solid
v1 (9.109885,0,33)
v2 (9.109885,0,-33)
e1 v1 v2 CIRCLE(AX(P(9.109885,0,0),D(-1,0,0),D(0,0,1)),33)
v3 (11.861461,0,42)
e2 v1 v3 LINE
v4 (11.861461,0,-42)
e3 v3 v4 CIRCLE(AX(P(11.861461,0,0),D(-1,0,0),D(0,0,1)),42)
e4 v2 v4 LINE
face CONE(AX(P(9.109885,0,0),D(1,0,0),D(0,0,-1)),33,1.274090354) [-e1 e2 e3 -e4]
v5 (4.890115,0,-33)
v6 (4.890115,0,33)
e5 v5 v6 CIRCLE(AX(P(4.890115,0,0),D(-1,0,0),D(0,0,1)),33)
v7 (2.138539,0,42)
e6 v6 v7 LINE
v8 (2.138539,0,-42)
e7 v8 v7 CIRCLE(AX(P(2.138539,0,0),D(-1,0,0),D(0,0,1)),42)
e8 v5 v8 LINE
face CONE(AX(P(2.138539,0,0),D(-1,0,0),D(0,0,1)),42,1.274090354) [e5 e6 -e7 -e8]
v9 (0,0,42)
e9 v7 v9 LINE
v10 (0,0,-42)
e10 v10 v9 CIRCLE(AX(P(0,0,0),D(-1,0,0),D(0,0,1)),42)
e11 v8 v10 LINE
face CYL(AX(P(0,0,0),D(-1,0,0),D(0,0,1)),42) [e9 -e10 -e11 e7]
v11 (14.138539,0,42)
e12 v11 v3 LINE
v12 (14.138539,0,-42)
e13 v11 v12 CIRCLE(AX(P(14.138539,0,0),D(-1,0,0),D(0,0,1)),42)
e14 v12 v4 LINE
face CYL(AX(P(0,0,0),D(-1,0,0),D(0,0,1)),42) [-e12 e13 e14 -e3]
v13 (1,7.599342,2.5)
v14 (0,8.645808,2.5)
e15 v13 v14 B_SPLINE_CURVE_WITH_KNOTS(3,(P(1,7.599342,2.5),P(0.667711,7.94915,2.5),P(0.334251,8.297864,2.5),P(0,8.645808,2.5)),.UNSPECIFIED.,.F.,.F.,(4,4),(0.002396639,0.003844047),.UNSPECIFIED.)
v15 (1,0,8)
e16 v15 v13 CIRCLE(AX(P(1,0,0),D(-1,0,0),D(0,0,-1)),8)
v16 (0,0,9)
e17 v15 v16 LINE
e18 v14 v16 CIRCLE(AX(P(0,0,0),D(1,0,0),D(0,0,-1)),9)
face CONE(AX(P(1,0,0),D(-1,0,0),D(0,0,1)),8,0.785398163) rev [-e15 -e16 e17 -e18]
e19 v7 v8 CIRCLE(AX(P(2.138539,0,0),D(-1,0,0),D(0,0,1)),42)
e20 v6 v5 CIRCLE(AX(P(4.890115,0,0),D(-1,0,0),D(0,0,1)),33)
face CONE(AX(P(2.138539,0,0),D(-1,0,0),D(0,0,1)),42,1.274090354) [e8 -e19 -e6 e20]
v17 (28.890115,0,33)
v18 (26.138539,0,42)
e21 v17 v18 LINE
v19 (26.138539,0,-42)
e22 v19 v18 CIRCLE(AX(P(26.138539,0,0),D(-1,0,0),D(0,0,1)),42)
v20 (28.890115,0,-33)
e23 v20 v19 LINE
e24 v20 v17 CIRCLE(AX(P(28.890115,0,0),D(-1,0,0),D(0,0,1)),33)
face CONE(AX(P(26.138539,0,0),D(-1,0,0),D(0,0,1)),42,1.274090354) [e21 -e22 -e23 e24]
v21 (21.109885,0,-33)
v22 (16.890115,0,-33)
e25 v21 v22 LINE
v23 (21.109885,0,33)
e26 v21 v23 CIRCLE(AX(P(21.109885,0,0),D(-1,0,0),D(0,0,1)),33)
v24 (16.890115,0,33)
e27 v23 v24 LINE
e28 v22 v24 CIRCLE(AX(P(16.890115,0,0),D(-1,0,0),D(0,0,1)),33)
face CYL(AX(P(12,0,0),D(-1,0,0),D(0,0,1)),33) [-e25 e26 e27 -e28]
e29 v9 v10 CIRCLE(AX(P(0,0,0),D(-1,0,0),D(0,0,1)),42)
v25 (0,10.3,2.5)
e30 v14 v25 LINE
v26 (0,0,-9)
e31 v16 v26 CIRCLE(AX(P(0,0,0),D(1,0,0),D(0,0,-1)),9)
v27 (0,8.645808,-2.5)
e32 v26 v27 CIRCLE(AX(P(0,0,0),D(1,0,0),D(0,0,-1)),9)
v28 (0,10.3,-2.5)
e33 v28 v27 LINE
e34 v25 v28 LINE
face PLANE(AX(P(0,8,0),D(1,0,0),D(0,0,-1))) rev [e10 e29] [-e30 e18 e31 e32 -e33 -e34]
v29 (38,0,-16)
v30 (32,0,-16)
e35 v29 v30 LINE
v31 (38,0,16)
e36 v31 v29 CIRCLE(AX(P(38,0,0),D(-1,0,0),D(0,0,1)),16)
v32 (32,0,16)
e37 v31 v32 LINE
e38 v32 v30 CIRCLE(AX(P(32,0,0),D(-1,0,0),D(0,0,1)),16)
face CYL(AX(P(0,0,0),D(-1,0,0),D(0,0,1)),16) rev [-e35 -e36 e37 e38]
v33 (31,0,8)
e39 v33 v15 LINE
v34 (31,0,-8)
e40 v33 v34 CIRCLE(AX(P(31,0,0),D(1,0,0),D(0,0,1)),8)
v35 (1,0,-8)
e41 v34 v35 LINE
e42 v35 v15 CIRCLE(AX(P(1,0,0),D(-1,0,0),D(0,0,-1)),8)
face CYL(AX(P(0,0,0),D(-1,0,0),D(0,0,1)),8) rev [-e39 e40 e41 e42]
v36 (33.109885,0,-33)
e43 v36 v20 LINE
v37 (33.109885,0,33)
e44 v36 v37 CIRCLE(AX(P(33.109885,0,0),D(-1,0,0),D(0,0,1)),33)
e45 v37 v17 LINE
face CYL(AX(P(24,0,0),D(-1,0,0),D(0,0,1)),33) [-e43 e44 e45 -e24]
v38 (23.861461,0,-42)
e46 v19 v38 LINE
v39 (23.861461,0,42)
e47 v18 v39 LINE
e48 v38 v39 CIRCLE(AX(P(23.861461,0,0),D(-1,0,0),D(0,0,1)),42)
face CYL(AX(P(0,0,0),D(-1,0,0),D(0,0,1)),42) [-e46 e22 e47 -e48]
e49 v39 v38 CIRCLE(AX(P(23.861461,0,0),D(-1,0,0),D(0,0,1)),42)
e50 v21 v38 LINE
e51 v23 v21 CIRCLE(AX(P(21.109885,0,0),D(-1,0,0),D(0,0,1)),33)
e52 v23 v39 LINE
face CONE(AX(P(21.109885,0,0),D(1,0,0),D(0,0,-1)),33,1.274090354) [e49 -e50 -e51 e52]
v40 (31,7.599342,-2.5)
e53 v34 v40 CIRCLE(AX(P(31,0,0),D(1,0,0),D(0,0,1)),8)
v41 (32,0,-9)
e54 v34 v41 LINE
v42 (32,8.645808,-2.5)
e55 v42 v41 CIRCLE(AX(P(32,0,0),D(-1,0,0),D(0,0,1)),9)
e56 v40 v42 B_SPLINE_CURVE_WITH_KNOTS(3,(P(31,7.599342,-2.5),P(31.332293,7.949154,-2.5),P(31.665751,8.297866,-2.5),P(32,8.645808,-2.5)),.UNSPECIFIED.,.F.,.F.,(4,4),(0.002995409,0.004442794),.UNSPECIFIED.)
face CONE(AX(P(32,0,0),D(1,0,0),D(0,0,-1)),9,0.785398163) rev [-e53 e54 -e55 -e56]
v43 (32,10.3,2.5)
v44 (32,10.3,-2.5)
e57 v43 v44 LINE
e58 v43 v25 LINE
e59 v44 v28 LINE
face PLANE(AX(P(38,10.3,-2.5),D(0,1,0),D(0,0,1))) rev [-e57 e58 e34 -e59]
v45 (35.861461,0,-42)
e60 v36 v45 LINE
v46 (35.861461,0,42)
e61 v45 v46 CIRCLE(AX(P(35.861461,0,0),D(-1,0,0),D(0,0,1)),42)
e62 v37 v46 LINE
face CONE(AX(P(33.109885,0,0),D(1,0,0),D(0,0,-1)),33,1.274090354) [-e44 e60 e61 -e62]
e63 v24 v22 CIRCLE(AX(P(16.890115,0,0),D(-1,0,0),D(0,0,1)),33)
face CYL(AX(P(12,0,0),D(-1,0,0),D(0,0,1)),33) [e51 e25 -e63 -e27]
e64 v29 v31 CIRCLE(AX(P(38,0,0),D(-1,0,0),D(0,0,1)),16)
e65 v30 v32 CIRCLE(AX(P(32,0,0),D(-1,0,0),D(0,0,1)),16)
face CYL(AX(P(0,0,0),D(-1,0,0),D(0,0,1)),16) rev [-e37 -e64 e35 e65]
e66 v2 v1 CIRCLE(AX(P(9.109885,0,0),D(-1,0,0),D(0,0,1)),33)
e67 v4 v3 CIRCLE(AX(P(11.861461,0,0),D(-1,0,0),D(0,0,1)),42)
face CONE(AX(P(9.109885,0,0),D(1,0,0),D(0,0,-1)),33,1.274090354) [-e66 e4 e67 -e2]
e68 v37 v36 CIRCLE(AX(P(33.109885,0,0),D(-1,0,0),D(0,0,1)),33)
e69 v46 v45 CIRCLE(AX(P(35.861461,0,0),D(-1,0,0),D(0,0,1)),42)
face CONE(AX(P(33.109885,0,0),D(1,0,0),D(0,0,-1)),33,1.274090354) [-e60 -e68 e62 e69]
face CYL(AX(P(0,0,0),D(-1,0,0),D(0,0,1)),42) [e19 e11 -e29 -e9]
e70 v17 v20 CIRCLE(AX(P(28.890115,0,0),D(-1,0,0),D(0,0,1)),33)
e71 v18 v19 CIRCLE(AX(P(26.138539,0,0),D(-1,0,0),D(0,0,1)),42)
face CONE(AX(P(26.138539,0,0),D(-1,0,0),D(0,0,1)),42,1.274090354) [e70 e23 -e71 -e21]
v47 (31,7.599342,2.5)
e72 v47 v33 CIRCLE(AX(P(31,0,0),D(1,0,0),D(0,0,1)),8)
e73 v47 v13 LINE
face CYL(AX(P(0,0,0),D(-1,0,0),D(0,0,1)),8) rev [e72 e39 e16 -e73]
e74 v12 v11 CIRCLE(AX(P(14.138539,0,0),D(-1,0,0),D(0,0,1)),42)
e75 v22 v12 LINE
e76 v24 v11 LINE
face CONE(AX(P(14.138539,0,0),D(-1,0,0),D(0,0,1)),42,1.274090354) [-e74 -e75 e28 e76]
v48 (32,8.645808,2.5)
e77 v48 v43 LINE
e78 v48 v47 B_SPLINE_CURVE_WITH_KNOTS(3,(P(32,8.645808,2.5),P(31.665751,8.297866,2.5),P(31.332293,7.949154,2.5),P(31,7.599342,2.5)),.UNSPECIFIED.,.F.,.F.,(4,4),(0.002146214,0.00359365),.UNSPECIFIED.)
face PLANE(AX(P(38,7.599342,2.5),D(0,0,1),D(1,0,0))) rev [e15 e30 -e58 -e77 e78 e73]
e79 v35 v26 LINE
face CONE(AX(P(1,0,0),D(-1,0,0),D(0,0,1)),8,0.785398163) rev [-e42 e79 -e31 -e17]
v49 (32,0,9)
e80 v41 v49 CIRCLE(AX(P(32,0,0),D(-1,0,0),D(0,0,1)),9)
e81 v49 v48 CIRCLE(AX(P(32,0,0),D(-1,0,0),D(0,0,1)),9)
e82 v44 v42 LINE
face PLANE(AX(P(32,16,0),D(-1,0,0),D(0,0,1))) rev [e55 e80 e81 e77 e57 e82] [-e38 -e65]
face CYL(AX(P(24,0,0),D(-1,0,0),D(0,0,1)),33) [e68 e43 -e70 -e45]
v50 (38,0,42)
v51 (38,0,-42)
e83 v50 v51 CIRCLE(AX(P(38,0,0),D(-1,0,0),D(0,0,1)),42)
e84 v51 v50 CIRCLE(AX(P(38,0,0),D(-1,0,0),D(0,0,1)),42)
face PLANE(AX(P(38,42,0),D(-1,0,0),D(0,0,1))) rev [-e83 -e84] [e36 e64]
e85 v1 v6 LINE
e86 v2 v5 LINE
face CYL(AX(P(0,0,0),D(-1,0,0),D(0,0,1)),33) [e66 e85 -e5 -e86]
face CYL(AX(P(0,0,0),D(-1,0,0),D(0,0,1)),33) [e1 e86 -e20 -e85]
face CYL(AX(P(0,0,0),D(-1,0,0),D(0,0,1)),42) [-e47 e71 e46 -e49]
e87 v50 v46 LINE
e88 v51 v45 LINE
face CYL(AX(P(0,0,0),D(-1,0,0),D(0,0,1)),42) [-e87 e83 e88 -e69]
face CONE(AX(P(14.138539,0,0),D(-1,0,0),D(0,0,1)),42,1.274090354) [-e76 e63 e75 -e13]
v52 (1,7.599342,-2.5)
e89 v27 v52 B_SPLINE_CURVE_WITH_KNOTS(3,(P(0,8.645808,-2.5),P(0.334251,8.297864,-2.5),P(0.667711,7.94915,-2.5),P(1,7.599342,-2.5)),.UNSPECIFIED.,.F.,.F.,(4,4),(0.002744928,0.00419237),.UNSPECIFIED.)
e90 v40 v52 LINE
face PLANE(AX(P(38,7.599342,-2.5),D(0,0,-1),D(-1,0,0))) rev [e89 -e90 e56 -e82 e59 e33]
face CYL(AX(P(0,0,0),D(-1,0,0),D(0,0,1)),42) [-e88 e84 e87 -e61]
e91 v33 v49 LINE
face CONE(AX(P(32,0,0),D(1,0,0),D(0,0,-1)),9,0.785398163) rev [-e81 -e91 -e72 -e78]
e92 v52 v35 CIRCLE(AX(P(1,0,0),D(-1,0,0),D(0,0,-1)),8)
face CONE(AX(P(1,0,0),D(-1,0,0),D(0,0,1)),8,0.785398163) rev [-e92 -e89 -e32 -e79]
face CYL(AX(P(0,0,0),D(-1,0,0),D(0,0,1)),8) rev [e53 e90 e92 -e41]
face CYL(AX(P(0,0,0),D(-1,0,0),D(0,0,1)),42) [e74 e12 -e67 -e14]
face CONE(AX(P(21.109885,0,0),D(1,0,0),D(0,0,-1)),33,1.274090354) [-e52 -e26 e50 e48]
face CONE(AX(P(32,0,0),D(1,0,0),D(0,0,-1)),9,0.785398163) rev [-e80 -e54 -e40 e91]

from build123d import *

# Parameters (mm, degrees)
PATTERN_LINEAR_1_COUNT = 3
PATTERN_LINEAR_1_PITCH = 12
CHAMFER_1_SIZE         = 1
SKETCH_4_W             = 5
SKETCH_4_H             = 2.700657875
CUT_EXTRUDE_1_DEPTH    = 71.512410255


with BuildPart() as part:
    # 草图1 → 旋转1 (revolve)
    with BuildSketch(Plane.XY, mode=Mode.PRIVATE) as revolve_1_sk:
        Polygon((0, 8), (0, 42), (38, 42), (38, 16), (32, 16), (32, 8), align=None)
    revolve(revolve_1_sk.sketch.rotate(Axis((0, 0, 0), (1, 0, 0)), 90), axis=Axis((0, 0, 0), (1, 0, 0)))

    # 草图2 → 切除-旋转1 (revolve, cut)
    with BuildSketch(Plane.XY, mode=Mode.PRIVATE) as cut_revolve_1_sk:
        Polygon((9.10988523, 33), (11.861461363, 42), (2.138538637, 42), (4.89011477, 33), align=None)
    cut_revolve_1 = revolve(cut_revolve_1_sk.sketch.rotate(Axis((0, 0, 0), (1, 0, 0)), 90), axis=Axis((0, 0, 0), (1, 0, 0)), mode=Mode.SUBTRACT)

    # 阵列(线性)1: 切除-旋转1 ×3
    with Locations(*[(i * PATTERN_LINEAR_1_PITCH, 0, 0) for i in range(1, PATTERN_LINEAR_1_COUNT)]):
        add(cut_revolve_1, mode=Mode.SUBTRACT)

    # 倒角1
    chamfer_1_edges = [part.edges().sort_by_distance(p)[0] for p in [
        (32, 0, -8),
        (0, 0, -8),
    ]]
    chamfer(chamfer_1_edges, length=CHAMFER_1_SIZE)

    # 草图4 → 切除-拉伸1 (cut, through all)
    with BuildSketch(Plane.ZY):
        with Locations((0, 8.949671014)):
            Rectangle(SKETCH_4_W, SKETCH_4_H)
    extrude(amount=-CUT_EXTRUDE_1_DEPTH, mode=Mode.SUBTRACT)


solid = part.part
